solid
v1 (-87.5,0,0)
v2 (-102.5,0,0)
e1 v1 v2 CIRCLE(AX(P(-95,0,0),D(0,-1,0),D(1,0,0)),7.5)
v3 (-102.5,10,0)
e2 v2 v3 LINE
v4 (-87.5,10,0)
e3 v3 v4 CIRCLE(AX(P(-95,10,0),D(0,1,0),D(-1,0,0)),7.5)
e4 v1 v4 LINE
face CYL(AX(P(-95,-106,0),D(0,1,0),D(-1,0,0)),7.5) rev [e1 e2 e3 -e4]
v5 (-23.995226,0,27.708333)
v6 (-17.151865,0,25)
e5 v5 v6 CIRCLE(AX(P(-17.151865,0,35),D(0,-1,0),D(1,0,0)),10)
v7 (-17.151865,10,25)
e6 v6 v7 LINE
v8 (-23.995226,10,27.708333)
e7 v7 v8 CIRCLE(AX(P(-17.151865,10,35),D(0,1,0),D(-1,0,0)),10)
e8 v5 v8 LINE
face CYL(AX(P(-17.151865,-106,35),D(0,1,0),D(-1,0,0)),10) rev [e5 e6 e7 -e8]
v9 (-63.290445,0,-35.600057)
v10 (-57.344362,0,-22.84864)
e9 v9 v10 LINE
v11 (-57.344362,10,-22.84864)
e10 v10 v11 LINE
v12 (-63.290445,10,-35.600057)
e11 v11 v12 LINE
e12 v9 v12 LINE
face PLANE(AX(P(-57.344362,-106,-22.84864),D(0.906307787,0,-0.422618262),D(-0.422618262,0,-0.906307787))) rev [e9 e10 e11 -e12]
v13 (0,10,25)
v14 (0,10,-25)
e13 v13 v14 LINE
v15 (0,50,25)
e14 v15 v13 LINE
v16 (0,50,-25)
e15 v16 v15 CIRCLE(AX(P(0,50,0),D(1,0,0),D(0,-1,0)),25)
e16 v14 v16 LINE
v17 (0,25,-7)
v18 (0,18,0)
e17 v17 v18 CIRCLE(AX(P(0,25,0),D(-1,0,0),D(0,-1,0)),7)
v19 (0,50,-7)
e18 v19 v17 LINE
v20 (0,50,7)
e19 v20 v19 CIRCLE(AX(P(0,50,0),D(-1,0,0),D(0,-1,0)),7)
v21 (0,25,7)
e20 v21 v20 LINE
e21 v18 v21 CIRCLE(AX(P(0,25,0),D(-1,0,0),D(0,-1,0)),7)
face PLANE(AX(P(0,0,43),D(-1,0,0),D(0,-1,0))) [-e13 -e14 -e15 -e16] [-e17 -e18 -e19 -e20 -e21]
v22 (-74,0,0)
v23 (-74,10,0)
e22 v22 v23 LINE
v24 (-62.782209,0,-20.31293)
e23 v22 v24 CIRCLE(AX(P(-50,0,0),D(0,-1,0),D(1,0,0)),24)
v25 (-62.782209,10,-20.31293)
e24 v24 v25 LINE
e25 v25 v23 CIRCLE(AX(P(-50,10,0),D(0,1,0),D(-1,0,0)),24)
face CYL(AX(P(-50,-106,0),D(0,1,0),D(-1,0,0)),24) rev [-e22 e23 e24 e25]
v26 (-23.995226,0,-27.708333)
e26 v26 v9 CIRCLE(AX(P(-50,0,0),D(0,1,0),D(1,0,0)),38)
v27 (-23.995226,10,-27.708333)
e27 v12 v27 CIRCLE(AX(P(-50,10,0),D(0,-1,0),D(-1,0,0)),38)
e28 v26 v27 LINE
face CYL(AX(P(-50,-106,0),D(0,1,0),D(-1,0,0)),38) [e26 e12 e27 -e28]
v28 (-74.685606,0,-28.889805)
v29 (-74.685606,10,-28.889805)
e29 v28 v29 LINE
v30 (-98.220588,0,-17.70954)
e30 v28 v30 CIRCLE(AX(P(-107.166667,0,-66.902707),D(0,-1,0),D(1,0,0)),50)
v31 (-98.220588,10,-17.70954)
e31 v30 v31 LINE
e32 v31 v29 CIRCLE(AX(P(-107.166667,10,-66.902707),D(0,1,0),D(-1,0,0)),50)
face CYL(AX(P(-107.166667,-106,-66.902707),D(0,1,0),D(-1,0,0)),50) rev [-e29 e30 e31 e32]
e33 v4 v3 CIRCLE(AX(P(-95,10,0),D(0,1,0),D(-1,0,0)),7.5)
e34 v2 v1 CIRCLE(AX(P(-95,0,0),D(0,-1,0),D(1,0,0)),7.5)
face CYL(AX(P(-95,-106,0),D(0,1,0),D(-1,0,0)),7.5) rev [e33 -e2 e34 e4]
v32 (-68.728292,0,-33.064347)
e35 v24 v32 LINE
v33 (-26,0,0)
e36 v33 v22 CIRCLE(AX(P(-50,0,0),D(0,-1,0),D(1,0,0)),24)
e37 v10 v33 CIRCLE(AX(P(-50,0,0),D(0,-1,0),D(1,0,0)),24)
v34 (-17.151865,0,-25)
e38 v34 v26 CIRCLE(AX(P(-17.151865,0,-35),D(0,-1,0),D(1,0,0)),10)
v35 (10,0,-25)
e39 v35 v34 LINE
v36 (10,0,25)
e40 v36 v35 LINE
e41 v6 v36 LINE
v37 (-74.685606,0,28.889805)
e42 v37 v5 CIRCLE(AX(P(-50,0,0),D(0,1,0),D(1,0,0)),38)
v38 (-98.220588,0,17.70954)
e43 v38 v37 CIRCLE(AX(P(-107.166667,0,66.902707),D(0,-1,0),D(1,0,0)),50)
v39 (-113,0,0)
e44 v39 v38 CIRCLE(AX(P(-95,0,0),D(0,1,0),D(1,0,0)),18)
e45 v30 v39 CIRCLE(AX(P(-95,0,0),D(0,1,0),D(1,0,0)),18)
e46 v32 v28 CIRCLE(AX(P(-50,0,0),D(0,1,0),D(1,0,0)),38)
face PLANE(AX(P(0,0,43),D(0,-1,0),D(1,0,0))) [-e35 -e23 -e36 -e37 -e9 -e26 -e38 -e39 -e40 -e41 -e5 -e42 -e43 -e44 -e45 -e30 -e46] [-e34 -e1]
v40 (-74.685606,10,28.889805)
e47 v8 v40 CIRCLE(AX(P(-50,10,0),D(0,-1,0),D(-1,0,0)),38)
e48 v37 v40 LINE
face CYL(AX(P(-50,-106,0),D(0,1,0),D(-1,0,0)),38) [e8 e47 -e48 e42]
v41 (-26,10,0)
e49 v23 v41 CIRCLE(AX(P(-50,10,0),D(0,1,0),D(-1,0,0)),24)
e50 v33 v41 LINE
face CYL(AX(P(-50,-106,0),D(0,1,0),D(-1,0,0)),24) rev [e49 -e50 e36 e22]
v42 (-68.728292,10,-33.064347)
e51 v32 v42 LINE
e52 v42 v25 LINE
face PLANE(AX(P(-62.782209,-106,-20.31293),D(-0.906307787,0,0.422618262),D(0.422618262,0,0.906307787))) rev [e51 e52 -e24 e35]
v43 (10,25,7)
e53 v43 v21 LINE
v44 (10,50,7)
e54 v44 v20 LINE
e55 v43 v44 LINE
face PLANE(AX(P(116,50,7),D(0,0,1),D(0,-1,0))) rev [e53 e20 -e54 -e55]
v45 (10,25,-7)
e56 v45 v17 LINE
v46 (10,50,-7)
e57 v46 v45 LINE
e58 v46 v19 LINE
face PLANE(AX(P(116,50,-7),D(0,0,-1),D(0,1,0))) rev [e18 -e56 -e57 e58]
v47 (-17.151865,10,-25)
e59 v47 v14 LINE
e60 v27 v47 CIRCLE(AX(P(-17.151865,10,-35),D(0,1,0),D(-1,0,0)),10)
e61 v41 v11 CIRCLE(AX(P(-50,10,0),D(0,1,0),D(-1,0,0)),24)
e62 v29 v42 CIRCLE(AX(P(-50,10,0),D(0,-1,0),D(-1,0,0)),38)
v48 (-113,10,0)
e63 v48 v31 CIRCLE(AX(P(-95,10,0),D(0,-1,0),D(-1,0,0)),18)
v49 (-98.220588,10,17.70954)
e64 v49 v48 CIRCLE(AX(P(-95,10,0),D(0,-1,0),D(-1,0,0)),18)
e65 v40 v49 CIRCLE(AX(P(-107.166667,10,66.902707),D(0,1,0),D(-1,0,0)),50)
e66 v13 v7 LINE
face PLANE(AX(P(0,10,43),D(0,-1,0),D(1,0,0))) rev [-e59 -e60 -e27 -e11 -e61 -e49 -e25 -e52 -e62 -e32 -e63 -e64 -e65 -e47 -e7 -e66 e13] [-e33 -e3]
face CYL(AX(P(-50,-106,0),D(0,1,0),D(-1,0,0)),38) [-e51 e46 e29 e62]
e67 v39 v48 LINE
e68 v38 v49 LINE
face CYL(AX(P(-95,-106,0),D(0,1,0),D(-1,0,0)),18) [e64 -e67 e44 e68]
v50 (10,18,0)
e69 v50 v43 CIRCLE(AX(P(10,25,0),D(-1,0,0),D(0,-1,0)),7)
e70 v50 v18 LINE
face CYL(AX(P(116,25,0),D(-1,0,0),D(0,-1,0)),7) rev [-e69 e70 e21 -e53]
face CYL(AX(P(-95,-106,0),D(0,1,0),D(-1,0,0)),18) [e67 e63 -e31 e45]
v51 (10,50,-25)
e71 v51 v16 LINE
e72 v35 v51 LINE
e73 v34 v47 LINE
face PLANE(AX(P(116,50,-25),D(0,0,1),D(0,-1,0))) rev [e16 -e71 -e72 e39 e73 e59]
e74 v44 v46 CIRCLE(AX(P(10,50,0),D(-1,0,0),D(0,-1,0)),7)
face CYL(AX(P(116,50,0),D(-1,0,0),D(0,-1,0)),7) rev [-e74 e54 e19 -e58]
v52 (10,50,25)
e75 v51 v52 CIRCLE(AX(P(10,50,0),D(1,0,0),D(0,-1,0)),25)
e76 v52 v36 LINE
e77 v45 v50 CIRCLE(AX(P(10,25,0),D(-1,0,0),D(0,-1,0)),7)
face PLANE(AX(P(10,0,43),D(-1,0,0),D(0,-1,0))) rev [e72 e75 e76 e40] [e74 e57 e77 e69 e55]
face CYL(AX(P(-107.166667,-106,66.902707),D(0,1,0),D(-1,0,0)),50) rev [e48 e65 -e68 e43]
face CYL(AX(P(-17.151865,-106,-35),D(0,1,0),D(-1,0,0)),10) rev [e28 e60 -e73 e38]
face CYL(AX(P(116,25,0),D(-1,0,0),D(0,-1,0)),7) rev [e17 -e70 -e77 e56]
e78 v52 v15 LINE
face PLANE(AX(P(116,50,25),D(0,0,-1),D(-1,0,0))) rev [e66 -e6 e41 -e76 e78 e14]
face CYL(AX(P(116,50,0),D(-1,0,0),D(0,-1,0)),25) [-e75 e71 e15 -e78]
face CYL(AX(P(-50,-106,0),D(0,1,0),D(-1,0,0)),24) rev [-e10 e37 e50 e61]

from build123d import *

# Parameters (mm, degrees)
L_ANGLE_PROFILE_SKETCH_W       = 150
L_ANGLE_PROFILE_SKETCH_H       = 10
L_ANGLE_PROFILE_SKETCH_W_2     = 10
L_ANGLE_PROFILE_SKETCH_H_2     = 100
L_ANGLE_BASE_DEPTH             = 43
UPRIGHT_TAB_AND_SLOT_CUT_DEPTH = 116
CLAMP_ARM_PROFILE_SKETCH_R     = 7.5
CLAMP_ARM_PROFILE_CUT_DEPTH    = 116


with BuildPart() as part:
    # L-Angle Profile Sketch → L-Angle Base (new, symmetric)
    with BuildSketch(Plane.XY):
        with Locations((-75, 5)):
            Rectangle(L_ANGLE_PROFILE_SKETCH_W, L_ANGLE_PROFILE_SKETCH_H)
        with Locations((5, 50)):
            Rectangle(L_ANGLE_PROFILE_SKETCH_W_2, L_ANGLE_PROFILE_SKETCH_H_2)
    extrude(amount=L_ANGLE_BASE_DEPTH, both=True)

    # Upright Tab and Slot Sketch → Upright Tab and Slot Cut (cut)
    with BuildSketch(Plane.ZY):
        with BuildLine():
            Line((7, 50), (7, 25))
            ThreePointArc((7, 25), (0, 18), (-7, 25))
            Line((-7, 25), (-7, 50))
            ThreePointArc((-7, 50), (0, 57), (7, 50))
        make_face()
        with BuildLine():
            Line((-25, 50), (-25, 10))
            Line((-25, 10), (-59.506944139, 10))
            Line((-59.506944139, 10), (-59.506944139, 107.254315339))
            Line((-59.506944139, 107.254315339), (43, 107.254315339))
            Line((43, 107.254315339), (43, 10))
            Line((43, 10), (25, 10))
            Line((25, 10), (25, 50))
            ThreePointArc((25, 50), (0, 75), (-25, 50))
        make_face()
    extrude(amount=-UPRIGHT_TAB_AND_SLOT_CUT_DEPTH, mode=Mode.SUBTRACT)

    # Clamp Arm Profile Sketch → Clamp Arm Profile Cut (cut)
    with BuildSketch(Plane(origin=(0, 10, 0), x_dir=(1, 0, 0), z_dir=(0, 1, 0))):
        with Locations(Location((-95, 0, 0), (0, 0, 180))):
            Circle(CLAMP_ARM_PROFILE_SKETCH_R)
        with BuildLine():
            Line((10, -25), (10, -43))
            Line((10, -43), (-150, -43))
            Line((-150, -43), (-150, 43))
            Line((-150, 43), (10, 43))
            Line((10, 43), (10, 25))
            Line((10, 25), (-17.151864589, 25))
            ThreePointArc((-17.151864589, 25), (-20.83176495, 25.701702665), (-23.995226133, 27.708333333))
            ThreePointArc((-23.995226133, 27.708333333), (-42.517796957, 37.256095308), (-63.29044546, 35.600057015))
            Line((-63.29044546, 35.600057015), (-57.34436202, 22.848639927))
            ThreePointArc((-57.34436202, 22.848639927), (-39.857161718, -21.751386889), (-62.782208742, 20.312930357))
            Line((-62.782208742, 20.312930357), (-68.728292182, 33.064347445))
            ThreePointArc((-68.728292182, 33.064347445), (-71.807070885, 31.119955968), (-74.685606061, 28.889805354))
            ThreePointArc((-74.685606061, 28.889805354), (-85.712027428, 21.739686255), (-98.220588235, 17.709540124))
            ThreePointArc((-98.220588235, 17.709540124), (-113, 0), (-98.220588235, -17.709540124))
            ThreePointArc((-98.220588235, -17.709540124), (-85.712027428, -21.739686255), (-74.685606061, -28.889805354))
            ThreePointArc((-74.685606061, -28.889805354), (-49.114550984, -37.989682547), (-23.995226133, -27.708333333))
            ThreePointArc((-23.995226133, -27.708333333), (-20.83176495, -25.701702665), (-17.151864589, -25))
            Line((-17.151864589, -25), (10, -25))
        make_face()
    extrude(amount=-CLAMP_ARM_PROFILE_CUT_DEPTH, mode=Mode.SUBTRACT)


solid = part.part
